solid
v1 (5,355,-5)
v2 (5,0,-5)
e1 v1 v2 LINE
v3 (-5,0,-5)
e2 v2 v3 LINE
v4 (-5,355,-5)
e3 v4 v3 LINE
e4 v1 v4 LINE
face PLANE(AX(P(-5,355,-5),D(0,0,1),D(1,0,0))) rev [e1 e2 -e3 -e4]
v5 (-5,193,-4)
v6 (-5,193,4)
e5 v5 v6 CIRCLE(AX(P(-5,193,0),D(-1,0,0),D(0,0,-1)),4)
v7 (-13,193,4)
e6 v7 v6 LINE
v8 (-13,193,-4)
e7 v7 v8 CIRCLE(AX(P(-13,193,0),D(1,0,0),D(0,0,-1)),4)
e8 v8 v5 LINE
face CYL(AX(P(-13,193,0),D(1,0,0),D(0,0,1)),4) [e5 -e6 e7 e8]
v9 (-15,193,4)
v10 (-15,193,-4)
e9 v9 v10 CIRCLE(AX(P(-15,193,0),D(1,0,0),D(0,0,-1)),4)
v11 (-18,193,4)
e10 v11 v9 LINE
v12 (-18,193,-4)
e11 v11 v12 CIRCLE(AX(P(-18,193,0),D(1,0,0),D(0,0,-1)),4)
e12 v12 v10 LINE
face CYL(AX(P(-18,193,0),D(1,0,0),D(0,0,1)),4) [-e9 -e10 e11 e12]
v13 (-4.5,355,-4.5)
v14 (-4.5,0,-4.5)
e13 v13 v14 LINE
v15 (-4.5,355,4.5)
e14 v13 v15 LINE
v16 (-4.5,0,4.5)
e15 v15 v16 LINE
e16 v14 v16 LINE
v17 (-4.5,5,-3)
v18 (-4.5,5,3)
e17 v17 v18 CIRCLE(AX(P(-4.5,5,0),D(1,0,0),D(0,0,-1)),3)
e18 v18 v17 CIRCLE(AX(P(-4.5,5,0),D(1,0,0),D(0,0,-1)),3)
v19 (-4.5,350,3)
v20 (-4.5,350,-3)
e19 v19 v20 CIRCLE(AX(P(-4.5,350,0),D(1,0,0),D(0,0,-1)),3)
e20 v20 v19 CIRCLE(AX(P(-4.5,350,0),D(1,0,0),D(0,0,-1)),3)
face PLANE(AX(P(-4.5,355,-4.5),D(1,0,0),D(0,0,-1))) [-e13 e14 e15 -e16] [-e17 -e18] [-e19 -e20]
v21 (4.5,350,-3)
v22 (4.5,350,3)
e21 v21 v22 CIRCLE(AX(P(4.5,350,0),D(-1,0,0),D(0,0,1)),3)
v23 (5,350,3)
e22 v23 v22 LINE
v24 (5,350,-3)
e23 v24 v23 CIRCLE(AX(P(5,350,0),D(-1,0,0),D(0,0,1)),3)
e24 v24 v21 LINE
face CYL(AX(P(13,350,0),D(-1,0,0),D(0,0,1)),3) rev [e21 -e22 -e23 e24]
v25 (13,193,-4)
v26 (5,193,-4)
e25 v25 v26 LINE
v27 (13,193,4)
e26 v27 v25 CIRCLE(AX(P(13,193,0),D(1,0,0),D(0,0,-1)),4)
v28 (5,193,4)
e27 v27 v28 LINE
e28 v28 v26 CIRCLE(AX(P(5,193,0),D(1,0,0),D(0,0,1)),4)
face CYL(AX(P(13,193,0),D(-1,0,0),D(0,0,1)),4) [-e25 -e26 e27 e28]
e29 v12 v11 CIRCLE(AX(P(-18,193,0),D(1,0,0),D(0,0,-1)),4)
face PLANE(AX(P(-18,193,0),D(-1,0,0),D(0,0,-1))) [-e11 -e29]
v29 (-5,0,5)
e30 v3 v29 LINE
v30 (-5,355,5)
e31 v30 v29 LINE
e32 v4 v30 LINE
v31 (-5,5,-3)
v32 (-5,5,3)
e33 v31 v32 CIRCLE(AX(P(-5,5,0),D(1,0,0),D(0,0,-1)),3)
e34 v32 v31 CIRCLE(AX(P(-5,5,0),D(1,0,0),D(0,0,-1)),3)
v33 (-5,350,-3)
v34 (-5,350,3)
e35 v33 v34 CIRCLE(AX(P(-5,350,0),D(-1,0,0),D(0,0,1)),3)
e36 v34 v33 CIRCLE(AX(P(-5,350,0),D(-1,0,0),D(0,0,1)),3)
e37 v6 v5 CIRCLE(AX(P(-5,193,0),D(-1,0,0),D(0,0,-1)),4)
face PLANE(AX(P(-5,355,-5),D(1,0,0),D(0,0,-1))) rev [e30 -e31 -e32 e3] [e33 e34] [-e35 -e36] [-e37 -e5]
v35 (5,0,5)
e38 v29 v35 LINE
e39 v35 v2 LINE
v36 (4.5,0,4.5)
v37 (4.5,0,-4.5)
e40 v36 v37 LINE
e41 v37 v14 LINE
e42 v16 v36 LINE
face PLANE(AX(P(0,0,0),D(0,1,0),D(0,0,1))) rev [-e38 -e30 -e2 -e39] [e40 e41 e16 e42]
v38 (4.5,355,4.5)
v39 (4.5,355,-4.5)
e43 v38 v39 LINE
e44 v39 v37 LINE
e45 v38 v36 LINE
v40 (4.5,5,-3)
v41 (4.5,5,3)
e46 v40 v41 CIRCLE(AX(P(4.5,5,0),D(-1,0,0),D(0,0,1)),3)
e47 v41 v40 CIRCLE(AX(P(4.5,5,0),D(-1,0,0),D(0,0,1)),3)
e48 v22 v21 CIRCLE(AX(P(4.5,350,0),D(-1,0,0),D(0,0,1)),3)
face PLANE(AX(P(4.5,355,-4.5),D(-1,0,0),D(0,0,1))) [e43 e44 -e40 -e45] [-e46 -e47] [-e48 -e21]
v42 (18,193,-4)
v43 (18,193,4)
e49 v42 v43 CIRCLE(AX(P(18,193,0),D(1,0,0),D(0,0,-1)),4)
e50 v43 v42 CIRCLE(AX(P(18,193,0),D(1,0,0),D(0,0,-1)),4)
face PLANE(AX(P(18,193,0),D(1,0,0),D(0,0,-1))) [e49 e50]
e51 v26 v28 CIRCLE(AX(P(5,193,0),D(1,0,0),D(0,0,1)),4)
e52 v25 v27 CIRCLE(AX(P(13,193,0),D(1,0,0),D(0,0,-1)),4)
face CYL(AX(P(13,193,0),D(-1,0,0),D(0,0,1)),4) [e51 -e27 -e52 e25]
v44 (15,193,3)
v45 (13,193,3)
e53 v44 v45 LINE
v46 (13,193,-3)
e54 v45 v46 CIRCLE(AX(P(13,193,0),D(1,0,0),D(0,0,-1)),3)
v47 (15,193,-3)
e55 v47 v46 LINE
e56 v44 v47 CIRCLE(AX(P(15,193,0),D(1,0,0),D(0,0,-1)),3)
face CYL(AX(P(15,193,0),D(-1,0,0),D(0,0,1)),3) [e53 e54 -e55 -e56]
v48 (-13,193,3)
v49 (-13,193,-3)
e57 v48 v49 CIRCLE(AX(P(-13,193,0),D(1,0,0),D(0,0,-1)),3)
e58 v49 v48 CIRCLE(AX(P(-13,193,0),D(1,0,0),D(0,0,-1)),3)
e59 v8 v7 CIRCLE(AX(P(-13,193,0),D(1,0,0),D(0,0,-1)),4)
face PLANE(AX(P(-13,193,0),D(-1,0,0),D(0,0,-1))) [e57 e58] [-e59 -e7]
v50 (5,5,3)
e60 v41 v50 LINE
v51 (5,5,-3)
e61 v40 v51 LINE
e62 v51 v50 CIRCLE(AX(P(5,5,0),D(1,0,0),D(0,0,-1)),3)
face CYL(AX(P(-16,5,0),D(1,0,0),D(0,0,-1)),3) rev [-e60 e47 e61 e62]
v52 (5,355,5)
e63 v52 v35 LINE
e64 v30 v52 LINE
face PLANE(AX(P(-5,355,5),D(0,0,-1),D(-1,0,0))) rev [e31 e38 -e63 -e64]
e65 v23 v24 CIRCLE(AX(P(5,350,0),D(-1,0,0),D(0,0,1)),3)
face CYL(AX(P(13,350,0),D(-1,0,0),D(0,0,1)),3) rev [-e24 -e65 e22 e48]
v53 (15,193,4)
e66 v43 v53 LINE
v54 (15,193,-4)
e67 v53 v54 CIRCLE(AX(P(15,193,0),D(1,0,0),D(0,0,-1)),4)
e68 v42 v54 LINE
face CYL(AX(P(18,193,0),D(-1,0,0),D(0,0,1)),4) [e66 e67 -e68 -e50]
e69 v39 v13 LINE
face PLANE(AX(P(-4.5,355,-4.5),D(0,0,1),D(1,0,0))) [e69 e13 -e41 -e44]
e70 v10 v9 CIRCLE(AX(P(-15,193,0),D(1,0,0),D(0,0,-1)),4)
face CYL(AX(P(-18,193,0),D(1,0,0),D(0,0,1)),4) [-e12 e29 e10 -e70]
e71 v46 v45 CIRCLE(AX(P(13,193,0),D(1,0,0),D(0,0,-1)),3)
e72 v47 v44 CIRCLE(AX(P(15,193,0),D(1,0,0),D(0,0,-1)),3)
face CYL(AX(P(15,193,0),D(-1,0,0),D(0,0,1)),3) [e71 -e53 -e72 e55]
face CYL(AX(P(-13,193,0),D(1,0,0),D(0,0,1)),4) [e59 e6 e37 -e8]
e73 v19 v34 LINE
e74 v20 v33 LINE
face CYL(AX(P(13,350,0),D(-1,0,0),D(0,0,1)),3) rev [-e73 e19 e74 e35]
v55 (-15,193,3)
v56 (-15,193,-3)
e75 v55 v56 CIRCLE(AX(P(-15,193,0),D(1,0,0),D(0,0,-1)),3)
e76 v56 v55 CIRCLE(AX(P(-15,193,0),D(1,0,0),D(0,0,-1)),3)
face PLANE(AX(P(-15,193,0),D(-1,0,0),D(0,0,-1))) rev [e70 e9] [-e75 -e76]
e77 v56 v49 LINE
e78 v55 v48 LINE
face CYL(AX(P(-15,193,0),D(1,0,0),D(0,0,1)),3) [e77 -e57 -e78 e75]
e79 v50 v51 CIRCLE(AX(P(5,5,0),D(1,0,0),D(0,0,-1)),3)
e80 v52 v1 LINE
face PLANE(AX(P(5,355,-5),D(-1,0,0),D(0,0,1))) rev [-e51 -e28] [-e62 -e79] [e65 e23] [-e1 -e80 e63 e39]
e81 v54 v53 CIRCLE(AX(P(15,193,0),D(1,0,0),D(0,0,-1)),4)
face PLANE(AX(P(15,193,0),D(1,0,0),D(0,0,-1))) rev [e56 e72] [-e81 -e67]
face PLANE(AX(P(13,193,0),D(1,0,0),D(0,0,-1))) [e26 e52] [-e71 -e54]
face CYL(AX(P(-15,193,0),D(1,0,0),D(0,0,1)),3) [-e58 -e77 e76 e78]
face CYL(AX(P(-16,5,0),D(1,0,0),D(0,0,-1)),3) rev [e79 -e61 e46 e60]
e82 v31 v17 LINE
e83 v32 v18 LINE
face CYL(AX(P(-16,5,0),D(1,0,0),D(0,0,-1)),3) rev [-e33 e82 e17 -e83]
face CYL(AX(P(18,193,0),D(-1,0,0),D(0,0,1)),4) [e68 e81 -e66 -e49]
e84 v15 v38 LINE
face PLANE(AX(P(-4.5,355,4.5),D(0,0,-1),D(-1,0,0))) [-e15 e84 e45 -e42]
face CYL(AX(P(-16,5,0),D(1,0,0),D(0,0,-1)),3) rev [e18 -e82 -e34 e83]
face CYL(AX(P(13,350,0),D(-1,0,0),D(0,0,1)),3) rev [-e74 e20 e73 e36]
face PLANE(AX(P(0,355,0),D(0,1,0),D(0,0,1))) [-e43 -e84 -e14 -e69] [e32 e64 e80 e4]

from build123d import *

# Parameters (mm, degrees)
SKETCH1_W           = 10
SKETCH1_H           = 10
SKETCH1_W_2         = 9
SKETCH1_H_2         = 9
BOSS_EXTRUDE1_DEPTH = 355
SKETCH2_R           = 4
BOSS_EXTRUDE2_DEPTH = 8
SKETCH3_R           = 3
BOSS_EXTRUDE3_DEPTH = 2
SKETCH4_R           = 4
BOSS_EXTRUDE4_DEPTH = 3
SKETCH5_R           = 3
CUT_EXTRUDE1_DEPTH  = 21
SKETCH6_R           = 3
CUT_EXTRUDE2_DEPTH  = 18


with BuildPart() as part:
    # Sketch1 → Boss-Extrude1 (new body)
    with BuildSketch(Plane(origin=(0, 0, 0), x_dir=(1, 0, 0), z_dir=(0, 1, 0))):
        Rectangle(SKETCH1_W, SKETCH1_H)
        Rectangle(SKETCH1_W_2, SKETCH1_H_2, mode=Mode.SUBTRACT)
    extrude(amount=BOSS_EXTRUDE1_DEPTH)

    # Sketch2 → Boss-Extrude2 (add)
    with BuildSketch(Plane(origin=(5, 0, 0), x_dir=(0, 0, -1), z_dir=(1, 0, 0))):
        with Locations(Location((0, 193, 0), (0, 0, 180))):
            Circle(SKETCH2_R)
    extrude(amount=BOSS_EXTRUDE2_DEPTH)

    # Sketch3 → Boss-Extrude3 (add)
    with BuildSketch(Plane(origin=(13, 0, 0), x_dir=(0, 0, -1), z_dir=(1, 0, 0))):
        with Locations((0, 193)):
            Circle(SKETCH3_R)
    extrude(amount=BOSS_EXTRUDE3_DEPTH)

    # Sketch4 → Boss-Extrude4 (add)
    with BuildSketch(Plane(origin=(15, 0, 0), x_dir=(0, 0, -1), z_dir=(1, 0, 0))):
        with Locations(Location((0, 193, 0), (0, 0, 180))):
            Circle(SKETCH4_R)
    extrude(amount=BOSS_EXTRUDE4_DEPTH)

    # Mirror1: part across plane


with BuildPart() as part_1:
    add(part.part)
    add(part.part.mirror(Plane(origin=(0, 0, 0), x_dir=(0, 0, 1), z_dir=(1, 0, 0))))

    # Sketch5 → Cut-Extrude1 (cut)
    with BuildSketch(Plane(origin=(5, 0, 0), x_dir=(0, 0, -1), z_dir=(1, 0, 0))):
        with Locations((0, 5)):
            Circle(SKETCH5_R)
    extrude(amount=-CUT_EXTRUDE1_DEPTH, mode=Mode.SUBTRACT)

    # Sketch6 → Cut-Extrude2 (cut)
    with BuildSketch(Plane.ZY.offset(5)):
        with Locations((0, 350)):
            Circle(SKETCH6_R)
    extrude(amount=-CUT_EXTRUDE2_DEPTH, mode=Mode.SUBTRACT)


solid = part_1.part
